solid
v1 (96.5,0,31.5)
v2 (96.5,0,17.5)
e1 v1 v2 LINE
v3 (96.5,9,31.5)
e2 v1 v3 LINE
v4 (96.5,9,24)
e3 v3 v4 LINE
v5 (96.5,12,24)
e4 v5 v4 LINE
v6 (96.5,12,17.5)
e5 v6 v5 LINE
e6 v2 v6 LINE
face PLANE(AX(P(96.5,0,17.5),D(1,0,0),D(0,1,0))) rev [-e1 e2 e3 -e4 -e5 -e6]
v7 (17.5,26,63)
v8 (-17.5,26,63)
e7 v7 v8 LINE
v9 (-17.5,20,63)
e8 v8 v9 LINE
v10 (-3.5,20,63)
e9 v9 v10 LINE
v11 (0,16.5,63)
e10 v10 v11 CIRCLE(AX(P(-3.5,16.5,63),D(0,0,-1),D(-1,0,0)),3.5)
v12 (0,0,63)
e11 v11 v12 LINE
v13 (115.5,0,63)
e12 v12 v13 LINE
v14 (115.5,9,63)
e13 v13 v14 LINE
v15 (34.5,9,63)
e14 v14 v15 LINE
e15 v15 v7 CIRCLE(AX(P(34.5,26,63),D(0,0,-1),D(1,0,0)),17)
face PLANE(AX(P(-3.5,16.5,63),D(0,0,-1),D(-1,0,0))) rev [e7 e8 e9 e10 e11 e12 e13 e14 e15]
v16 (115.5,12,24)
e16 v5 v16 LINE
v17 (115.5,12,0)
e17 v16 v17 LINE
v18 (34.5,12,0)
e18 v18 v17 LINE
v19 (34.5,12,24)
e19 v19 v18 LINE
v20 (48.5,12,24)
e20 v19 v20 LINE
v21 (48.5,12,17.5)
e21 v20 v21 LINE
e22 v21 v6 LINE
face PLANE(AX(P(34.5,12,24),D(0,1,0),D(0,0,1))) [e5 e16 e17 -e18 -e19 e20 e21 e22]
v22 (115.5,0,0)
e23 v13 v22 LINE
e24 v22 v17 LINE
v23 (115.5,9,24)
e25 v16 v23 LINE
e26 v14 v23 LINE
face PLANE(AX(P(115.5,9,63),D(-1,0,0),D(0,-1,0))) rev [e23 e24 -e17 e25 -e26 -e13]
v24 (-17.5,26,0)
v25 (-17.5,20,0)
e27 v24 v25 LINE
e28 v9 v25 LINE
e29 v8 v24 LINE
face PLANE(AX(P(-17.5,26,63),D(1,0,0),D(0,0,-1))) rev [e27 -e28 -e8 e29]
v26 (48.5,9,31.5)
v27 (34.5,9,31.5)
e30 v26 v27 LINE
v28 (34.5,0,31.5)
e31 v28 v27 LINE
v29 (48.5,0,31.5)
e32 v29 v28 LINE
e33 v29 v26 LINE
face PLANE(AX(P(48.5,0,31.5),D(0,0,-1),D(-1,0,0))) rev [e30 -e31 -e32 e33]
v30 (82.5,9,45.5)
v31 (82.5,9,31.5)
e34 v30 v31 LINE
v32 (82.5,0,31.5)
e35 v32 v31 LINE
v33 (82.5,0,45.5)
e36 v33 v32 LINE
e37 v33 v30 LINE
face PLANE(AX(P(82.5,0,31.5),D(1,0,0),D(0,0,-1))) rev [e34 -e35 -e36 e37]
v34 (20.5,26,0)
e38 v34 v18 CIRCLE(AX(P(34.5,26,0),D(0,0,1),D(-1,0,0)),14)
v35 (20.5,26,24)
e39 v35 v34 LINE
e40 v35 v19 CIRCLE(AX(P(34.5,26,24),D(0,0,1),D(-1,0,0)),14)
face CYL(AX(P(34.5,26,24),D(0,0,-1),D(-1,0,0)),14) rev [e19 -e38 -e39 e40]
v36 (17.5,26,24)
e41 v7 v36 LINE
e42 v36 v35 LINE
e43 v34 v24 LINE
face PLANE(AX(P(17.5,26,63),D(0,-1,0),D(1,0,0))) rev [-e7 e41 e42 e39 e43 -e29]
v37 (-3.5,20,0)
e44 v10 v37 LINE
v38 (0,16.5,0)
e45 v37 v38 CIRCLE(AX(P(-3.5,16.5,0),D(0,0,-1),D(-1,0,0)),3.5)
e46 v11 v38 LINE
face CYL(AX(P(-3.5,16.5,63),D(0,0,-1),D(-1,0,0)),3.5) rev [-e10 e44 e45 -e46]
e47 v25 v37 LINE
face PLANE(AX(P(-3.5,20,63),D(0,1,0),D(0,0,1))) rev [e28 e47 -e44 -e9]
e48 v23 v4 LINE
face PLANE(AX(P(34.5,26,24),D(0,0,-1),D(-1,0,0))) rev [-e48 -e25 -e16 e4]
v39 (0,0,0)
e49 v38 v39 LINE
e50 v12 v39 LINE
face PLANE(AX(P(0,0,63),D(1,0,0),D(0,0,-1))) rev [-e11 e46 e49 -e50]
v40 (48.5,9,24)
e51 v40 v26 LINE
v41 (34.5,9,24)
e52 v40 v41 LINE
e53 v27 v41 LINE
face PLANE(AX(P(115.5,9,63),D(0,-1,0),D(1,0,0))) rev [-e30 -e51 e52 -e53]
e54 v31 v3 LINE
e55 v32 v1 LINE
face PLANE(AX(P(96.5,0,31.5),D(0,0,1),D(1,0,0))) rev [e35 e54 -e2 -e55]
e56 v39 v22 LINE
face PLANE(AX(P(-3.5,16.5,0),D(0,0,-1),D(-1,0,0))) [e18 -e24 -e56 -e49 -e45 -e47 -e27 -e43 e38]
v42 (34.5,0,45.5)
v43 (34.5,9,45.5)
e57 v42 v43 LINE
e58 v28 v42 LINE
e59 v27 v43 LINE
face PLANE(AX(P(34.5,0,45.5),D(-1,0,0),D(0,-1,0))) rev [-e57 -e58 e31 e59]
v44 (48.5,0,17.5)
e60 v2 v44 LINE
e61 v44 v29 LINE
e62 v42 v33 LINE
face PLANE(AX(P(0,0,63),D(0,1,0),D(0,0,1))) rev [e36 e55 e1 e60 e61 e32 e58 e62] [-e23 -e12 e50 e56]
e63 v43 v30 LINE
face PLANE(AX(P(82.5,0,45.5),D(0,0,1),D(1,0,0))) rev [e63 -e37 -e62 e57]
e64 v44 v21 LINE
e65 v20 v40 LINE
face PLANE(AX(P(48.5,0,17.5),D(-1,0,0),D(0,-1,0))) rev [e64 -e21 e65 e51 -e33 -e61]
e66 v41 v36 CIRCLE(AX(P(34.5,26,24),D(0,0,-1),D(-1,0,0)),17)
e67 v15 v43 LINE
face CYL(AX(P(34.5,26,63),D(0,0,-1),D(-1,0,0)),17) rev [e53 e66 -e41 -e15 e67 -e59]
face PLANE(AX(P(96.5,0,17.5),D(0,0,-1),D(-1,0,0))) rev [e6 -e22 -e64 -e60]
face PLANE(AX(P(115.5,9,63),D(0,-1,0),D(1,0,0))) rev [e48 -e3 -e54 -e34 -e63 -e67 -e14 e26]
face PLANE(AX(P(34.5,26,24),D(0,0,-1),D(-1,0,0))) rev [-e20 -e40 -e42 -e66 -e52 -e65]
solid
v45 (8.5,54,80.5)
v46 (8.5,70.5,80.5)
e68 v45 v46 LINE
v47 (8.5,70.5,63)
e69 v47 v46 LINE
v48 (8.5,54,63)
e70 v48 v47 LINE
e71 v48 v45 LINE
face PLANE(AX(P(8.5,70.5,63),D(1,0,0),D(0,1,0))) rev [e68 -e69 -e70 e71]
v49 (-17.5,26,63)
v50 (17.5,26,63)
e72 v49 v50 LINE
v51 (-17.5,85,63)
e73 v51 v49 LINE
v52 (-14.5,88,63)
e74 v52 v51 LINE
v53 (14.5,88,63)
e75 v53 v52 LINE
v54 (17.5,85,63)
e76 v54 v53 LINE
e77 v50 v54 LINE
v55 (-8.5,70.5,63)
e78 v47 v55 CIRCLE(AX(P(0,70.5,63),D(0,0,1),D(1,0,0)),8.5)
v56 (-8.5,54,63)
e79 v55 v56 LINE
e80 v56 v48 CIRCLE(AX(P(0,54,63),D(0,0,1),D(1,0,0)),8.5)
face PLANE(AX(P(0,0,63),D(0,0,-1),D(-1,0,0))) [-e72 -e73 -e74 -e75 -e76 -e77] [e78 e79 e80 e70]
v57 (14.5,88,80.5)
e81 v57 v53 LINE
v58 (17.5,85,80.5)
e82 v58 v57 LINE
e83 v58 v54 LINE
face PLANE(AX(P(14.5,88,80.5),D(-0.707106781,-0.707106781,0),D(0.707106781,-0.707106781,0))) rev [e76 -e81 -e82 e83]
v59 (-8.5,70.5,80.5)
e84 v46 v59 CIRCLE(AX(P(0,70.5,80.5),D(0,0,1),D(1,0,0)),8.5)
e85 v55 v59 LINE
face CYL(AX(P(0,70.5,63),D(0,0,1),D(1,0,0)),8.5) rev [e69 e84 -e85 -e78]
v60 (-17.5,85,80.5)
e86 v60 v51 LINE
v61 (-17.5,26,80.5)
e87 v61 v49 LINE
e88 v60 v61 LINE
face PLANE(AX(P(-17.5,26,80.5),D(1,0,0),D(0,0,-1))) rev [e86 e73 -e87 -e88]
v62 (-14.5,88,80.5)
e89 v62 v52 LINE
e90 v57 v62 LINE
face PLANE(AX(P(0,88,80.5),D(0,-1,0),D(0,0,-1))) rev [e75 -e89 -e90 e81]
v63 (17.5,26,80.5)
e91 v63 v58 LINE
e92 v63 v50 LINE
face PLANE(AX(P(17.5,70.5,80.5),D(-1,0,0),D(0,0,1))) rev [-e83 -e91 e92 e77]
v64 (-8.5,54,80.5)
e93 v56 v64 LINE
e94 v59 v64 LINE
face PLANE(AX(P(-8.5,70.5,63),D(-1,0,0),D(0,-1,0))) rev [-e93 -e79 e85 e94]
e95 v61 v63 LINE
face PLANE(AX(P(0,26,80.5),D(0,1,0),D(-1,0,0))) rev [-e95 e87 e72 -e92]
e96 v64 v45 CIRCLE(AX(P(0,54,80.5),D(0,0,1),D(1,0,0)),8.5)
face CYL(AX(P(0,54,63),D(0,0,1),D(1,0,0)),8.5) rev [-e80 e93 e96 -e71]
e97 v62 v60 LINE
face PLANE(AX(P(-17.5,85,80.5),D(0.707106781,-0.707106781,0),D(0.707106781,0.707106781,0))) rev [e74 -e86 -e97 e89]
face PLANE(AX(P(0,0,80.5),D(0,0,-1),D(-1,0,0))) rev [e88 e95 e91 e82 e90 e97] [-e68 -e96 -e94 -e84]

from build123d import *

# Parameters (mm, degrees)
BASE_PLATE_DEPTH           = 63
UPRIGHT_BLOCK_DEPTH        = 17.5
UPRIGHT_OBROUND_SLOT_DEPTH = 17.5
STEPPED_WINDOW_CUT_DEPTH   = 9
RAISED_PAD_DEPTH           = 24
GROOVE_SKETCH_W            = 48
GROOVE_SKETCH_H            = 6.5
GROOVE_CUT_3MM_DEPTH       = 3


with BuildPart() as part:
    # Base Profile Sketch → Base Plate (new body)
    with BuildSketch(Plane.XY):
        with BuildLine():
            Line((0, 0), (115.5, 0))
            Line((115.5, 0), (115.5, 9))
            Line((115.5, 9), (34.5, 9))
            ThreePointArc((34.5, 9), (22.47918472, 13.97918472), (17.5, 26))
            Line((17.5, 26), (-17.5, 26))
            Line((-17.5, 26), (-17.5, 20))
            Line((-17.5, 20), (-3.5, 20))
            ThreePointArc((-3.5, 20), (-1.025126266, 18.974873734), (0, 16.5))
            Line((0, 16.5), (0, 0))
        make_face()
    extrude(amount=BASE_PLATE_DEPTH)

    # Stepped Window Sketch → Stepped Window Cut (cut)
    with BuildSketch(Plane(origin=(0, 9, 0), x_dir=(1, 0, 0), z_dir=(0, 1, 0))):
        Polygon((96.5, -17.5), (48.5, -17.5), (48.5, -31.5), (34.5, -31.5), (34.5, -45.5), (82.5, -45.5), (82.5, -31.5), (96.5, -31.5), align=None)
    extrude(amount=-STEPPED_WINDOW_CUT_DEPTH, mode=Mode.SUBTRACT)

    # Raised Pad Sketch → Raised Pad (add)
    with BuildSketch(Plane(origin=(0, 0, 0), x_dir=(-1, 0, 0), z_dir=(0, 0, -1))):
        with BuildLine():
            Line((-34.5, 12), (-115.5, 12))
            Line((-115.5, 12), (-115.5, 9))
            Line((-115.5, 9), (-34.5, 9))
            ThreePointArc((-34.5, 9), (-22.47918472, 13.97918472), (-17.5, 26))
            Line((-17.5, 26), (-20.5, 26))
            ThreePointArc((-20.5, 26), (-24.600505063, 16.100505063), (-34.5, 12))
        make_face()
    extrude(amount=-RAISED_PAD_DEPTH)

    # Groove Sketch → Groove Cut 3mm (cut)
    with BuildSketch(Plane.XZ.offset(-9)):
        with Locations((72.5, 20.75)):
            Rectangle(GROOVE_SKETCH_W, GROOVE_SKETCH_H)
    extrude(amount=-GROOVE_CUT_3MM_DEPTH, mode=Mode.SUBTRACT)


with BuildPart() as body_2:
    # Upright Block Sketch → Upright Block (new body)
    with BuildSketch(Plane.XY.offset(63)):
        Polygon((0, 26), (17.5, 26), (17.5, 54), (17.5, 70.5), (17.5, 85), (14.5, 88), (0, 88), (-14.5, 88), (-17.5, 85), (-17.5, 26), align=None)
    extrude(amount=UPRIGHT_BLOCK_DEPTH)

    # Upright Slot Sketch → Upright Obround Slot (cut)
    with BuildSketch(Plane.XY.offset(80.5)):
        with BuildLine():
            Line((-8.5, 70.5), (-8.5, 54))
            ThreePointArc((-8.5, 54), (0, 45.5), (8.5, 54))
            Line((8.5, 54), (8.5, 70.5))
            ThreePointArc((8.5, 70.5), (0, 79), (-8.5, 70.5))
        make_face()
    extrude(amount=-UPRIGHT_OBROUND_SLOT_DEPTH, mode=Mode.SUBTRACT)


solid = Compound([part.part, body_2.part])
